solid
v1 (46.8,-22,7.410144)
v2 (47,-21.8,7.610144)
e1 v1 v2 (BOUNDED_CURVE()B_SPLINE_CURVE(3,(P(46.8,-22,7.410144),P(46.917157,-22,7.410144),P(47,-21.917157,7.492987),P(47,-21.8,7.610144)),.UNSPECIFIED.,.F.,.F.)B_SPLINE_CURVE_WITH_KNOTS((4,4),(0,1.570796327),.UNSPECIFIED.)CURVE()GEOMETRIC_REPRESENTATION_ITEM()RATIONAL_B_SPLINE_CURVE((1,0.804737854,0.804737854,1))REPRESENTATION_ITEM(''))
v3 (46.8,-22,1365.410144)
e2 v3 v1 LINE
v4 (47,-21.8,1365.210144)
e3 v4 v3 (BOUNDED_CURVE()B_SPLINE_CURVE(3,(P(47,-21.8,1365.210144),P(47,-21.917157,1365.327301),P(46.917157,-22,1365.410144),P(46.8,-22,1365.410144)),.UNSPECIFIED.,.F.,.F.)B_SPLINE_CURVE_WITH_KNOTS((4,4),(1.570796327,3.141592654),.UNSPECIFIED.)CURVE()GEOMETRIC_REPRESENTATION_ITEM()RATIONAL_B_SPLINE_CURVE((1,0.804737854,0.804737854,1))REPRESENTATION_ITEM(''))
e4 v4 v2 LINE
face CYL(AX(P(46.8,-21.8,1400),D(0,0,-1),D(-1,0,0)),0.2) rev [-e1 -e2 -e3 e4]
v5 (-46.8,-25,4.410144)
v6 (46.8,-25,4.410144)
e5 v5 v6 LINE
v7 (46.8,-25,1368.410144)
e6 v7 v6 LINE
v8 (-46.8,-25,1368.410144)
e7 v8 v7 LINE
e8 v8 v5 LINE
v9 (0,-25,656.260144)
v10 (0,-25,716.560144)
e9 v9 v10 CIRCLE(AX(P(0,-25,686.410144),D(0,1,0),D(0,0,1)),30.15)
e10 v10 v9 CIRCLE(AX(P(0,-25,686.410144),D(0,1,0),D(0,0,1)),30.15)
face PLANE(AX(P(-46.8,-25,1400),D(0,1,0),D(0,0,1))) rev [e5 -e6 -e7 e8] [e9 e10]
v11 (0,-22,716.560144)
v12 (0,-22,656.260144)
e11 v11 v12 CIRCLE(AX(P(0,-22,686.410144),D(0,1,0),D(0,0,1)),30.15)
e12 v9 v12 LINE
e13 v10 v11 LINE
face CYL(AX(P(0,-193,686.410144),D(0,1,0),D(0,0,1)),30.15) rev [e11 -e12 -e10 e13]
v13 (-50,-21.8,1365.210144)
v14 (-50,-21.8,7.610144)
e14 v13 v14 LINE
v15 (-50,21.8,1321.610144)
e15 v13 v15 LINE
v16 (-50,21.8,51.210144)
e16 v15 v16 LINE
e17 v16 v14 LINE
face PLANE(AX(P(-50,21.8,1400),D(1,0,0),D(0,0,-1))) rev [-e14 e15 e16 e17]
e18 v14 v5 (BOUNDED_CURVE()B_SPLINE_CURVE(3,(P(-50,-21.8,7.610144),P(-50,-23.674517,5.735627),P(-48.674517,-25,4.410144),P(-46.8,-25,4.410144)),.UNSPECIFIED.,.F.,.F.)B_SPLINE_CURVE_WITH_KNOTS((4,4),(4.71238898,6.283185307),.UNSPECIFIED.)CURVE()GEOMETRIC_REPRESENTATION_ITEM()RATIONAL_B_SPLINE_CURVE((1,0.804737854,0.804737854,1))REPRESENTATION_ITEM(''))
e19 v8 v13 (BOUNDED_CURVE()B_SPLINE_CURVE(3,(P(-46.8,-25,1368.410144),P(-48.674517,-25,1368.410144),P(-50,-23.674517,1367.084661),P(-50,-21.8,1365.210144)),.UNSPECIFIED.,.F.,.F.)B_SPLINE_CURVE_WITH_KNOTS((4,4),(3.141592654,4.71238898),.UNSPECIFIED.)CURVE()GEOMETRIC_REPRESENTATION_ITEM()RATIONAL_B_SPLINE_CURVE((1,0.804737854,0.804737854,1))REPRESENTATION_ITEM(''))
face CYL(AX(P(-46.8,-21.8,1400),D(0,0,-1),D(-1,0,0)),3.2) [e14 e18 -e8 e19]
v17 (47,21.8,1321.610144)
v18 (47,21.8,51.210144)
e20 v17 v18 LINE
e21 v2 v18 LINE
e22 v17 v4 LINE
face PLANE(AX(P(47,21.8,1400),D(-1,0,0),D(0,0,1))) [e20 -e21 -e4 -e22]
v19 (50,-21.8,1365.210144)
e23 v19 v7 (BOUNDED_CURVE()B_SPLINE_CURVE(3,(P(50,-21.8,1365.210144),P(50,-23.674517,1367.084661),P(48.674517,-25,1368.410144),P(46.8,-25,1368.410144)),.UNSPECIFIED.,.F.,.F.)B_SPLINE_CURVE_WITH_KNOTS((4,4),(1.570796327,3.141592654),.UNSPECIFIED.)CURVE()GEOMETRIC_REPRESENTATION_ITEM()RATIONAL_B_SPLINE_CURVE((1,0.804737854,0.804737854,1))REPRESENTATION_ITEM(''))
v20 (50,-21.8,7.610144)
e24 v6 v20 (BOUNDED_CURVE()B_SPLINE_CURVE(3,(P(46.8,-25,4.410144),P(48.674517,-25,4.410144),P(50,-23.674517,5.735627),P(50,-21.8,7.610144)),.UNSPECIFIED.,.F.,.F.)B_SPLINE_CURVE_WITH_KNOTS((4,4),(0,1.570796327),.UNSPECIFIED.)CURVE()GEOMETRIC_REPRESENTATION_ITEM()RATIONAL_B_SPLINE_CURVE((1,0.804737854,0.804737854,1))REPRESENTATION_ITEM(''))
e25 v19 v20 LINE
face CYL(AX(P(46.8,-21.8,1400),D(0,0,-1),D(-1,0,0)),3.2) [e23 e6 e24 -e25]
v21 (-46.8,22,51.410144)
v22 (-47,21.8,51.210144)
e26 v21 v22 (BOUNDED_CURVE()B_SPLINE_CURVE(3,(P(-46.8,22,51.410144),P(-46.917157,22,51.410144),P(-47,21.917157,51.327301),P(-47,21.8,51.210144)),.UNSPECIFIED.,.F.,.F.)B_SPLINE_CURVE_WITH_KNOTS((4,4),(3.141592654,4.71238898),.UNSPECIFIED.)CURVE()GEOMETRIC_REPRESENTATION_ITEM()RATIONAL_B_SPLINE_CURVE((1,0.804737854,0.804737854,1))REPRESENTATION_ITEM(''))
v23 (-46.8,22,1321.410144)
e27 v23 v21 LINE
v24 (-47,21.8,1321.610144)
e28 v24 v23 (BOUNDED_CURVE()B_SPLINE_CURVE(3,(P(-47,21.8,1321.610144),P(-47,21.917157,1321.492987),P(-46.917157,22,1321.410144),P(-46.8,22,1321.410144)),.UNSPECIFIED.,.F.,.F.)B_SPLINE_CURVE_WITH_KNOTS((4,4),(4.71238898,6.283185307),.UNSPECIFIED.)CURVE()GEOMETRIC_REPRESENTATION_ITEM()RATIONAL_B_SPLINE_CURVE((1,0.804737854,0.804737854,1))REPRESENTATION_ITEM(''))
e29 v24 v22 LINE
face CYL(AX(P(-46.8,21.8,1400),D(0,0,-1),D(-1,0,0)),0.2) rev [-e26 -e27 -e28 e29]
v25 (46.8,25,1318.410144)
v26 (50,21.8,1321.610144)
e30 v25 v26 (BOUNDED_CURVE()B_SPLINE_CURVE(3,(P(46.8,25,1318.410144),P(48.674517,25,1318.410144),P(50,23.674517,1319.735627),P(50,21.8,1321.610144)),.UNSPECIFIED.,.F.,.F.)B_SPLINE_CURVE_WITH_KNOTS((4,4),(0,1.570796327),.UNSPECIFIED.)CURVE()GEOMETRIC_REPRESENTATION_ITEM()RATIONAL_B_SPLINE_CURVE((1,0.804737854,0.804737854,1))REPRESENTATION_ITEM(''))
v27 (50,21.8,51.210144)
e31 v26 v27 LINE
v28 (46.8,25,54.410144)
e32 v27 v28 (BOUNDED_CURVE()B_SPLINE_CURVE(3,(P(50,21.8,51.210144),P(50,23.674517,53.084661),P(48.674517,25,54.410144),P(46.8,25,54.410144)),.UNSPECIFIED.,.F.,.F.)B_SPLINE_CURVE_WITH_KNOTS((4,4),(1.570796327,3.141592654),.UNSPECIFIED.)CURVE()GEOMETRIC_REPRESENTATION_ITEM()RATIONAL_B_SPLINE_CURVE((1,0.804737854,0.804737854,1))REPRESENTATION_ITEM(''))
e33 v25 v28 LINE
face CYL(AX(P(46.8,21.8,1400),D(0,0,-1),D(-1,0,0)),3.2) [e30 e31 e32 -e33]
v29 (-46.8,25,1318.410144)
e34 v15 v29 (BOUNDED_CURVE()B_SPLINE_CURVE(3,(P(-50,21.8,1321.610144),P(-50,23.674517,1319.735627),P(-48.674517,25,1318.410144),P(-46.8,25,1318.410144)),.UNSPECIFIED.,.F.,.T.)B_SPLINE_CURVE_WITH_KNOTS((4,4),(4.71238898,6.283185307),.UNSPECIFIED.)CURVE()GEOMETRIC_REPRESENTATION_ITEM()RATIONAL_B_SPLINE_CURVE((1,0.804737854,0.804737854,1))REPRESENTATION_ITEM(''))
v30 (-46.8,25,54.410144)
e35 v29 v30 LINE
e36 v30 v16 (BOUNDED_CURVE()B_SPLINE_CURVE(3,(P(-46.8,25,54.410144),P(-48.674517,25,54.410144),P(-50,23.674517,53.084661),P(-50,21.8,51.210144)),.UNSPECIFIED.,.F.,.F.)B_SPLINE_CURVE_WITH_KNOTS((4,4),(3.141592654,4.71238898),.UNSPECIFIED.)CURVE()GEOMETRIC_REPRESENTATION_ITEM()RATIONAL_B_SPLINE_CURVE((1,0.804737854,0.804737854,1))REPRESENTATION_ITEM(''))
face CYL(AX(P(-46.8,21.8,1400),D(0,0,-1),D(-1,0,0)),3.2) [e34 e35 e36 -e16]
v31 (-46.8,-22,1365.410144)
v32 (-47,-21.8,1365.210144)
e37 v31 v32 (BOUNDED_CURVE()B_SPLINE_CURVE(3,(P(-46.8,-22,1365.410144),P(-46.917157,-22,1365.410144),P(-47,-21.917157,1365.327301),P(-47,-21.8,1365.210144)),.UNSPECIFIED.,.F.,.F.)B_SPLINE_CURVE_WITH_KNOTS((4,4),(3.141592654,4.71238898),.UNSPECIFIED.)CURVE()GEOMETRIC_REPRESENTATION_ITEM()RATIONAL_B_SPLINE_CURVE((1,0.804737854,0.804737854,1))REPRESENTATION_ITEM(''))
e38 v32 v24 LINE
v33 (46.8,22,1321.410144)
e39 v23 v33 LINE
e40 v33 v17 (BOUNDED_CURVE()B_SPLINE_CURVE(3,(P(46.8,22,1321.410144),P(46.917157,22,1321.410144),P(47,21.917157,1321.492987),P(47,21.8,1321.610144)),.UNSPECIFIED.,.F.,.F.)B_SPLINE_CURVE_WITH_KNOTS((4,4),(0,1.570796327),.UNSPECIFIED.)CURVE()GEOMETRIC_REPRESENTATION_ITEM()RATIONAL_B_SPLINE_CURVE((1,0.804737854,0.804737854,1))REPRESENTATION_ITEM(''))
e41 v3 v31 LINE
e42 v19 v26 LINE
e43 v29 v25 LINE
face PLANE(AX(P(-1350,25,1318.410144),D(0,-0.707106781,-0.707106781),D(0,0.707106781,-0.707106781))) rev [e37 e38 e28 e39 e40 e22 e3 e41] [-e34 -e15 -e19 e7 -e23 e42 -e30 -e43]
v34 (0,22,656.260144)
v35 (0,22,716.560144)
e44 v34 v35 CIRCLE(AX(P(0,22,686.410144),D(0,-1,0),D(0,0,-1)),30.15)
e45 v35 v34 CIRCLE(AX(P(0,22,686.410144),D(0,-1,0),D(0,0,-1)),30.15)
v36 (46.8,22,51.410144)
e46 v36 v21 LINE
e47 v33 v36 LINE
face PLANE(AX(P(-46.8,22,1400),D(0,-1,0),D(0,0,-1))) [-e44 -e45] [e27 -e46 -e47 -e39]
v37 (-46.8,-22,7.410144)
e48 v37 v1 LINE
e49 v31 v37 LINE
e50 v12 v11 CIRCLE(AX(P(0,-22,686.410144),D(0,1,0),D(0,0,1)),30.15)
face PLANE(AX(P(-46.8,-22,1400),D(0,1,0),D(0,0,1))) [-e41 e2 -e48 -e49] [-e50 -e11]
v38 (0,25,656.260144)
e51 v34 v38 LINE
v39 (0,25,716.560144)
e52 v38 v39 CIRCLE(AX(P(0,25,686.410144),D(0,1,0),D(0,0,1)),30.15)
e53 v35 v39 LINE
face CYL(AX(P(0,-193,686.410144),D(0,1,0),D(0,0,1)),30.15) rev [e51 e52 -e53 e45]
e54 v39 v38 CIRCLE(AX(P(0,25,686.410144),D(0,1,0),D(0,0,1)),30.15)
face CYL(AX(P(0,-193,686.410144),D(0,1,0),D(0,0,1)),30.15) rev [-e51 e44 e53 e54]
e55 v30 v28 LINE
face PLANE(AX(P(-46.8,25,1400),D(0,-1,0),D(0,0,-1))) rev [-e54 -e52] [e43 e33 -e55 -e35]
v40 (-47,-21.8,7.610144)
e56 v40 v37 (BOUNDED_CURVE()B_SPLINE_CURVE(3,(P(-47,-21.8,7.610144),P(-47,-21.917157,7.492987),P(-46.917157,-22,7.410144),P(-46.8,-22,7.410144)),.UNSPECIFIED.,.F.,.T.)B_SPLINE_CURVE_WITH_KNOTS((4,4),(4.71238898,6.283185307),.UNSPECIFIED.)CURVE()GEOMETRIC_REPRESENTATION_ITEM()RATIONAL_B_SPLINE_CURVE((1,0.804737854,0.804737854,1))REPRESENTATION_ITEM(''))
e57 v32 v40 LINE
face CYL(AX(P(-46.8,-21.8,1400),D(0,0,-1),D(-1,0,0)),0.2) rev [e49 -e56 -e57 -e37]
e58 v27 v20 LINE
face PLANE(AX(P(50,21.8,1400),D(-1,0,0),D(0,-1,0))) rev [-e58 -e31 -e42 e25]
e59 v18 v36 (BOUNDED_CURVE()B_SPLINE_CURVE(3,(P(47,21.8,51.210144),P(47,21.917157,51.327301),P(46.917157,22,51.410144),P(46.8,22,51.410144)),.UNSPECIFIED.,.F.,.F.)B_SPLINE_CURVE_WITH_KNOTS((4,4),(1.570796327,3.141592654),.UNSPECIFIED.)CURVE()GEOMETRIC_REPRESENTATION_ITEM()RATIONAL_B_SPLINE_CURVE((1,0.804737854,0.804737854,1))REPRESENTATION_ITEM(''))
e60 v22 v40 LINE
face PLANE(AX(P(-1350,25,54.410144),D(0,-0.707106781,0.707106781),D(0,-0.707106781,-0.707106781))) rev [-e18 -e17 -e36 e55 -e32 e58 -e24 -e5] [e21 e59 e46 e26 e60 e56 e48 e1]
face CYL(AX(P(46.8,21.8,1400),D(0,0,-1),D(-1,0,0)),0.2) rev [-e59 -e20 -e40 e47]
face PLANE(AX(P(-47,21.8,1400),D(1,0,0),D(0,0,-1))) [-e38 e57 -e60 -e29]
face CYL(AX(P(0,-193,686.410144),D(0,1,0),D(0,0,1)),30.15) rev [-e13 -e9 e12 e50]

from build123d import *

# Parameters (mm, degrees)
EXTRUDE_1_DEPTH     = 1400
CUT_EXTRUDE_1_DEPTH = 1400
SKETCH_3_R          = 30.15
CUT_EXTRUDE_2_DEPTH = 218


with BuildPart() as part:
    # 草图1 → 凸台-拉伸1 (new body)
    with BuildSketch(Plane.XY):
        with BuildLine():
            Line((-46.8, 25), (46.8, 25))
            ThreePointArc((46.8, 25), (49.0627417, 24.0627417), (50, 21.8))
            Line((50, 21.8), (50, -21.8))
            ThreePointArc((50, -21.8), (49.0627417, -24.0627417), (46.8, -25))
            Line((46.8, -25), (-46.8, -25))
            ThreePointArc((-46.8, -25), (-49.0627417, -24.0627417), (-50, -21.8))
            Line((-50, -21.8), (-50, 21.8))
            ThreePointArc((-50, 21.8), (-49.0627417, 24.0627417), (-46.8, 25))
        make_face()
        with BuildLine():
            Line((-46.8, 22), (46.8, 22))
            ThreePointArc((46.8, 22), (46.941421356, 21.941421356), (47, 21.8))
            Line((47, 21.8), (47, -21.8))
            ThreePointArc((47, -21.8), (46.941421356, -21.941421356), (46.8, -22))
            Line((46.8, -22), (-46.8, -22))
            ThreePointArc((-46.8, -22), (-46.941421356, -21.941421356), (-47, -21.8))
            Line((-47, -21.8), (-47, 21.8))
            ThreePointArc((-47, 21.8), (-46.941421356, 21.941421356), (-46.8, 22))
        make_face(mode=Mode.SUBTRACT)
    extrude(amount=EXTRUDE_1_DEPTH)

    # 草图2 → 切除-拉伸1 (cut)
    with BuildSketch(Plane(origin=(50, 0, 0), x_dir=(0, 0, -1), z_dir=(1, 0, 0))):
        Polygon((-1318.410144038, 25), (-1368.410144038, -25), (-1510.151659449, -71.563080947), (-1552.75637803, 36.507424721), align=None)
        Polygon((-54.410144038, 25), (-4.410144038, -25), (36.992690616, -46.405998122), (74.054919354, -20.164122041), (119.219041394, 25), (0, 63.525051138), align=None)
    extrude(amount=-CUT_EXTRUDE_1_DEPTH, mode=Mode.SUBTRACT)

    # 草图3 → 切除-拉伸2 (cut)
    with BuildSketch(Plane(origin=(0, 25, 0), x_dir=(1, 0, 0), z_dir=(0, 1, 0))):
        with Locations(Location((0, -686.410144038, 0), (0, 0, 270))):
            Circle(SKETCH_3_R)
    extrude(amount=-CUT_EXTRUDE_2_DEPTH, mode=Mode.SUBTRACT)


solid = part.part
